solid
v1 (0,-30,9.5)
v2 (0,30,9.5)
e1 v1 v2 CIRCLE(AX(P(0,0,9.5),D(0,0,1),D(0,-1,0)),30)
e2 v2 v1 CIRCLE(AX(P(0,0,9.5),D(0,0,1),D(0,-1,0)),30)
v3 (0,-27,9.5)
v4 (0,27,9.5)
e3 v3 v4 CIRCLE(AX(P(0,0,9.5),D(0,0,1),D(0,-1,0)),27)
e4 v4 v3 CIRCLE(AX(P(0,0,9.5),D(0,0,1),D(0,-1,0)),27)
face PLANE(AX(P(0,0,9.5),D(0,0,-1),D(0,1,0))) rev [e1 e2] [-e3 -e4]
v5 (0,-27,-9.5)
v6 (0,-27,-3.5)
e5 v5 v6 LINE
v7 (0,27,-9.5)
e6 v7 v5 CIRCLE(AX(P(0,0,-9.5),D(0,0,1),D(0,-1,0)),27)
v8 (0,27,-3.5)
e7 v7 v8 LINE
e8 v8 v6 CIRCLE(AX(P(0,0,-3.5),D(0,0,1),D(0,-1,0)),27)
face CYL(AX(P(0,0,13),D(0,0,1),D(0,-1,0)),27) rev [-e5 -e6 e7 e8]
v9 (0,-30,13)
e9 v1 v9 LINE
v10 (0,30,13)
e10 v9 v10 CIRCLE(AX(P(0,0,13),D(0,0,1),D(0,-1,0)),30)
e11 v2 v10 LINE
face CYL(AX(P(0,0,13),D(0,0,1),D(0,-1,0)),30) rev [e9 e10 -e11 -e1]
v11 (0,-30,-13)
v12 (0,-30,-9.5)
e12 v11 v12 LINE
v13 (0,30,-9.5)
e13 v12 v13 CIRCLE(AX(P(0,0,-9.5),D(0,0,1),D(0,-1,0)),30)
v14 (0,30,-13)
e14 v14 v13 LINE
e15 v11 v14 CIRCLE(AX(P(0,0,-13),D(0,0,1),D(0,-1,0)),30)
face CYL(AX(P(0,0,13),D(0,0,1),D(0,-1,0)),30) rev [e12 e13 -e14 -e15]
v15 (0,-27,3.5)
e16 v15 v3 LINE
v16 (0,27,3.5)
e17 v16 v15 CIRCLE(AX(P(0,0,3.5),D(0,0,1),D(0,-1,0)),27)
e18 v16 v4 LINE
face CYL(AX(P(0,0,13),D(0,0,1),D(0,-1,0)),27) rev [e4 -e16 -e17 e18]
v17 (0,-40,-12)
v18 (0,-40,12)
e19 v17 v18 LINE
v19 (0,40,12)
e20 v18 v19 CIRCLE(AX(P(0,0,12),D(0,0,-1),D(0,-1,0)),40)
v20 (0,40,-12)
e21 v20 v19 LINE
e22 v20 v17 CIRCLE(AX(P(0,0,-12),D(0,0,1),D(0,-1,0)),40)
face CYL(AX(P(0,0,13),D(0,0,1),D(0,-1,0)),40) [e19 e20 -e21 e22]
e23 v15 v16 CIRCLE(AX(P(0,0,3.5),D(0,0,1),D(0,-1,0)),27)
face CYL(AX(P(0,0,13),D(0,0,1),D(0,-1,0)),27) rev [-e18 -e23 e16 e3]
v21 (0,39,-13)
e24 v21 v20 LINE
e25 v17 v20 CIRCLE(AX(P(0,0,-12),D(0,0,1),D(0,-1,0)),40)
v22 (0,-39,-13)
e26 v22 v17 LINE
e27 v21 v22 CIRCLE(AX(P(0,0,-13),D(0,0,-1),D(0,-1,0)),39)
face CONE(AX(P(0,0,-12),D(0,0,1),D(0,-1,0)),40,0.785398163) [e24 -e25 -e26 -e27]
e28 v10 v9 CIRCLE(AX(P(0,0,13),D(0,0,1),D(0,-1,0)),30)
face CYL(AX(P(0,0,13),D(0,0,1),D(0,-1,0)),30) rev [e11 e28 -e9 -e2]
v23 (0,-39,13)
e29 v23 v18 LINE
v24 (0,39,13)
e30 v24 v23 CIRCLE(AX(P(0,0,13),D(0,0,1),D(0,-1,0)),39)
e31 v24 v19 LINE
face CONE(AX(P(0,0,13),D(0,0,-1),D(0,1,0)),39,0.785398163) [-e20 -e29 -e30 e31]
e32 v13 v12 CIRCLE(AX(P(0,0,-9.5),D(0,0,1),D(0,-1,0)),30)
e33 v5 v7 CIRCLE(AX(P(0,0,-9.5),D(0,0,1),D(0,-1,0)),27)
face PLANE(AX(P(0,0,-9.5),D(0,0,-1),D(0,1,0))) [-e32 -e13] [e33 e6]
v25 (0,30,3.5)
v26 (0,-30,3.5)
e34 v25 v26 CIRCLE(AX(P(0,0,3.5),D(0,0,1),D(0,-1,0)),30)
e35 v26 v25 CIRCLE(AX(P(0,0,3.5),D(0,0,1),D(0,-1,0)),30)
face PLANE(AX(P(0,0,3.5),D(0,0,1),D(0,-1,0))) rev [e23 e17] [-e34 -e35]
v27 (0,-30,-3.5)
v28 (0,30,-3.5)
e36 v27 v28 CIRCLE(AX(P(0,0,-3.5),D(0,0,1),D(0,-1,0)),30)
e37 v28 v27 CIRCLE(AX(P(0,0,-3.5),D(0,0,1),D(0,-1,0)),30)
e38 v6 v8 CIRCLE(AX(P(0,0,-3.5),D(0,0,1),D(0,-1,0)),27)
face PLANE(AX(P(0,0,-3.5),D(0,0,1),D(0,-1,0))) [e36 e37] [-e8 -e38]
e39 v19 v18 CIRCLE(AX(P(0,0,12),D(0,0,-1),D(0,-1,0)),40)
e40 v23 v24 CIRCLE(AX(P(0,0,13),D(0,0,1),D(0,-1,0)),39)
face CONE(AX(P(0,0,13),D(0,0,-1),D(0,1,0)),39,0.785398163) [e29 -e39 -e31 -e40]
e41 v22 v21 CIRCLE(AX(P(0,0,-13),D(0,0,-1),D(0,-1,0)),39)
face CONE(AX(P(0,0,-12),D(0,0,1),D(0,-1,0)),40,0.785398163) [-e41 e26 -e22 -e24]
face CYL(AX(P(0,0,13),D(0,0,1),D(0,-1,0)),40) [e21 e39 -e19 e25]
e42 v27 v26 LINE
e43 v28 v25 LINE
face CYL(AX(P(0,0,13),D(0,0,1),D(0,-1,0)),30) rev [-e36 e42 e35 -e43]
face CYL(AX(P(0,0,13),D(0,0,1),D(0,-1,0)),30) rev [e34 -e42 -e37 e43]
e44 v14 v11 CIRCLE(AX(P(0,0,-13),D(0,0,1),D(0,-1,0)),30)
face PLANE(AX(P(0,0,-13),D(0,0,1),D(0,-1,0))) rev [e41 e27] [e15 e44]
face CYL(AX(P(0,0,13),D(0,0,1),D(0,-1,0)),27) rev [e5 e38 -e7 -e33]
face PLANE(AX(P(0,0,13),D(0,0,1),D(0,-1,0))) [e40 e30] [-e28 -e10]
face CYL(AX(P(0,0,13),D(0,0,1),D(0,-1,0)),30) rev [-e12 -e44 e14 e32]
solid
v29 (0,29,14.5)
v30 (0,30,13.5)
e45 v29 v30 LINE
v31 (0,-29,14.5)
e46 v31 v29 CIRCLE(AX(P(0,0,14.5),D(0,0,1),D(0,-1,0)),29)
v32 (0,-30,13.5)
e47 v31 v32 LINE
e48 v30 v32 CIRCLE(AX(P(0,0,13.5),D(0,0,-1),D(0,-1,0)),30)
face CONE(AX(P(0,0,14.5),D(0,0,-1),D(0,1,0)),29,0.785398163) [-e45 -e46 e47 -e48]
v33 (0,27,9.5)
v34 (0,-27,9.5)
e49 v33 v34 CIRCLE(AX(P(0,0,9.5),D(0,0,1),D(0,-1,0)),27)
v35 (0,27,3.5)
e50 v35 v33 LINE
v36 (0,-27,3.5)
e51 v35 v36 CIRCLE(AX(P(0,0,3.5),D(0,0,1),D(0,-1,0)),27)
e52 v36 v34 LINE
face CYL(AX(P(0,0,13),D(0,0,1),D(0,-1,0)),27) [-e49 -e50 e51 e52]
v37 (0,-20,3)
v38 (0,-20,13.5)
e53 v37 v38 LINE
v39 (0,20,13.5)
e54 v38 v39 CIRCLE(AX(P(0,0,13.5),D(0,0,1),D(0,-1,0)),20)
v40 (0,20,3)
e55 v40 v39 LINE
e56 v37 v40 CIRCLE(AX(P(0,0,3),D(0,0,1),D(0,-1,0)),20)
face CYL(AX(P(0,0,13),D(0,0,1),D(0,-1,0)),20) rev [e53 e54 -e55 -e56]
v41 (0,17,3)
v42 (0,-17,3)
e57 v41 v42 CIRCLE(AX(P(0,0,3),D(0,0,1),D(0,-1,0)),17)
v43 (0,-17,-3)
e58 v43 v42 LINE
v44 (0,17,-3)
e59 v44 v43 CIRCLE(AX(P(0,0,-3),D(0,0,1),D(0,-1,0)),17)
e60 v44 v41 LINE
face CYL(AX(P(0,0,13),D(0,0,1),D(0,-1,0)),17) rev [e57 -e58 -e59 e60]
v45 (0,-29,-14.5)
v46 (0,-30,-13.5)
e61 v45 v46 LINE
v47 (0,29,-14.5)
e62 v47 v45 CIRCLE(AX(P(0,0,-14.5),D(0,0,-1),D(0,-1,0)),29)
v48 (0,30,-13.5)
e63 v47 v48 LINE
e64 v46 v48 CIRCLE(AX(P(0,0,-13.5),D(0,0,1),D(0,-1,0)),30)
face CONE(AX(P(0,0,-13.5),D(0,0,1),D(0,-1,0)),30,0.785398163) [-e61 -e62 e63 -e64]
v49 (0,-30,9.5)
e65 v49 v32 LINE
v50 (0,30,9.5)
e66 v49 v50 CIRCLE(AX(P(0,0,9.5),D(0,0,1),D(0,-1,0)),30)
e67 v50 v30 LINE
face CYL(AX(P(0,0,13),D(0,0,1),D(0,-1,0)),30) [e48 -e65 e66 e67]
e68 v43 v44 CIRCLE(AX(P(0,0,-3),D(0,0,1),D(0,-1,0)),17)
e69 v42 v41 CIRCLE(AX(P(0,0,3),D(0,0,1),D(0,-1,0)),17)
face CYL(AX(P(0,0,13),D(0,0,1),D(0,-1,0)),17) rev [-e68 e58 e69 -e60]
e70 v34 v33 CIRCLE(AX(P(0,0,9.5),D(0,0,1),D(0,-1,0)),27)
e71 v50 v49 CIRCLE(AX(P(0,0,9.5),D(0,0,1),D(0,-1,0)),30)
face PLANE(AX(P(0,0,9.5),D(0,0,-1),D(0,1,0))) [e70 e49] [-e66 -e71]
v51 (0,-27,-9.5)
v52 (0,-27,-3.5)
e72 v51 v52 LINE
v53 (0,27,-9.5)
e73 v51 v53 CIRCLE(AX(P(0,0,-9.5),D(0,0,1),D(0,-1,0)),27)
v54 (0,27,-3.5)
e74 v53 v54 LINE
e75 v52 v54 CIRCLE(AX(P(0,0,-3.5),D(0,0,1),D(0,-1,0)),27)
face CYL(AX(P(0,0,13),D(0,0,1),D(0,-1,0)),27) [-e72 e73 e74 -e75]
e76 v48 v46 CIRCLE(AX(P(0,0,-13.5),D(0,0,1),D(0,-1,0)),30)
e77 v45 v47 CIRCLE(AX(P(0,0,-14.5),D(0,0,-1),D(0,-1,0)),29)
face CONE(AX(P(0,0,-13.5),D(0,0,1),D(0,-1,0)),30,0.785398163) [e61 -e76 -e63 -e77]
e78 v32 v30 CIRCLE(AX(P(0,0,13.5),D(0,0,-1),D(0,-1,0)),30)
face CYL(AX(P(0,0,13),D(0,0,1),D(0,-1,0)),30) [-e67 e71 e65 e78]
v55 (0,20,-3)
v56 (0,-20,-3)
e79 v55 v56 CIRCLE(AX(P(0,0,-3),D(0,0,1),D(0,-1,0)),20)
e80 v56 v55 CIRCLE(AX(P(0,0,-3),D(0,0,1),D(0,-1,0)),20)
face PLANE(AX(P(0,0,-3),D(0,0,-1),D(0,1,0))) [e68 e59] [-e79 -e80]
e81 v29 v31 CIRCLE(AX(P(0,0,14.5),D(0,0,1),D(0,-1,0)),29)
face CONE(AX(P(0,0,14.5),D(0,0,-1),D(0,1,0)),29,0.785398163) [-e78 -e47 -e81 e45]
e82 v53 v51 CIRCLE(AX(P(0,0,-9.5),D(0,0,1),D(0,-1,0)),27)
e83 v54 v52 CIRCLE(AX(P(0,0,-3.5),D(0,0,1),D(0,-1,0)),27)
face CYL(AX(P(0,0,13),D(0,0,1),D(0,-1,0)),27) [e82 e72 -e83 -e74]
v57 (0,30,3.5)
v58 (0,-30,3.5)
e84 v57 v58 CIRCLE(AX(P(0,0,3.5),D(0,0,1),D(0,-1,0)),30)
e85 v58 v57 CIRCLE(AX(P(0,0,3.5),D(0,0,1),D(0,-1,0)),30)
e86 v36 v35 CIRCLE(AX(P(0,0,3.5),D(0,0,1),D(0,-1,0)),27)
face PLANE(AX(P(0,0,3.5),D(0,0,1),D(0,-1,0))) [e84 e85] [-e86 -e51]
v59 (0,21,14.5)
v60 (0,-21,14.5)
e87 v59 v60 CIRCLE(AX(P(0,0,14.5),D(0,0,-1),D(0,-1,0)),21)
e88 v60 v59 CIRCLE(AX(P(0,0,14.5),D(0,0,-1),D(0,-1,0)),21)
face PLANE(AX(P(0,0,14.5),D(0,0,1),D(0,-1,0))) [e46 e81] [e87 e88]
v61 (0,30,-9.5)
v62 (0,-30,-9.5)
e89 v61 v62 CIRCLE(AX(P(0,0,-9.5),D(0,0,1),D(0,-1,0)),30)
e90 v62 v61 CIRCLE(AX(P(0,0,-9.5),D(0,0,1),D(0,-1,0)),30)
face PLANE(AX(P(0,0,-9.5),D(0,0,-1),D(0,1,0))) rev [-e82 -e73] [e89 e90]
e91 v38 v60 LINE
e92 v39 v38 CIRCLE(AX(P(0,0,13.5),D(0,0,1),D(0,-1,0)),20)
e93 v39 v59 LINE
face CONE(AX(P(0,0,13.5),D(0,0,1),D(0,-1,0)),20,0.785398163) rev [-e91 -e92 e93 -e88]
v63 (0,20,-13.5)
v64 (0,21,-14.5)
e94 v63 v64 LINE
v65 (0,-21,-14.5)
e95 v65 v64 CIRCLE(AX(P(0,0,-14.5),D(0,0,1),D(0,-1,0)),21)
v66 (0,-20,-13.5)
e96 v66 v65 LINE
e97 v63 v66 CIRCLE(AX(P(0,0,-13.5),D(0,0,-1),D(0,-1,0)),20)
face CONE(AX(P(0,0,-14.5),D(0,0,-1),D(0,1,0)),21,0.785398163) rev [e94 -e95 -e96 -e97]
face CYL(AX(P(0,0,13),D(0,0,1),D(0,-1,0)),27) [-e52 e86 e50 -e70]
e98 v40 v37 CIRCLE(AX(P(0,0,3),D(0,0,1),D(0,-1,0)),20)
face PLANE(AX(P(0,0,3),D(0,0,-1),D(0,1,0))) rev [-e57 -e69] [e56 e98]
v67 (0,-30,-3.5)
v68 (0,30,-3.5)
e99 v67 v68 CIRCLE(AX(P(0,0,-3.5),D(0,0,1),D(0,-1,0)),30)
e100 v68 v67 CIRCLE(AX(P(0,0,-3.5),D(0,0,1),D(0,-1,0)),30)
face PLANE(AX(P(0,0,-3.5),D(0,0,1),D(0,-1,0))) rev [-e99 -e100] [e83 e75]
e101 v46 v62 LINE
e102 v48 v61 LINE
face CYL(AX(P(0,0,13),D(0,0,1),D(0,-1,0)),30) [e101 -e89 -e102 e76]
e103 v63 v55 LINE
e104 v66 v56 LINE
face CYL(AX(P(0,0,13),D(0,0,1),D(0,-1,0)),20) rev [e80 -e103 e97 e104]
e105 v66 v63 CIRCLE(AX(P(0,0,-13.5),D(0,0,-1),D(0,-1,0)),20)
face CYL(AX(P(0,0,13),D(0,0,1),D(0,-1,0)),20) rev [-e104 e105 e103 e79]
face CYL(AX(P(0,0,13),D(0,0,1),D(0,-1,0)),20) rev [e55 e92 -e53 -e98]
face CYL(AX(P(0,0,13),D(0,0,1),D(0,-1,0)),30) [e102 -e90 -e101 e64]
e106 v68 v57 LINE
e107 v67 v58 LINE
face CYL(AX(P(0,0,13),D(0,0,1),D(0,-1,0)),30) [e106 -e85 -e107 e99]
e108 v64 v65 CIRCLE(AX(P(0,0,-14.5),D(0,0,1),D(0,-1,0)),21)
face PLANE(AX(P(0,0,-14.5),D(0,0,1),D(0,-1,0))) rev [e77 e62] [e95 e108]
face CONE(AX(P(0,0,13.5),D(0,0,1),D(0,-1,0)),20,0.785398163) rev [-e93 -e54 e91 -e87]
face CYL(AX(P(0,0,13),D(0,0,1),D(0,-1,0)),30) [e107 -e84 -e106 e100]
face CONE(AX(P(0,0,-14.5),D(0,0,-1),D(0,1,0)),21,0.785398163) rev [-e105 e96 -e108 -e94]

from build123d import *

# Parameters (mm, degrees)
SKETCH_1_3_2_W = 1.5
SKETCH_1_3_2_H = 10
CHAMFER1_SIZE  = 1
CHAMFER2_SIZE  = 1


with BuildPart() as part:
    # Sketch 1_3 → Revolve1 (revolve)
    with BuildSketch(Plane(origin=(0, 0, 0), x_dir=(0, 0, -1), z_dir=(1, 0, 0)), mode=Mode.PRIVATE) as revolve1_sk:
        Polygon((-13, 40), (-13, 30), (-9.5, 30), (-9.5, 27), (-3.5, 27), (-3.5, 30), (3.5, 30), (3.5, 27), (9.5, 27), (9.5, 30), (13, 30), (13, 40), align=None)
    revolve(revolve1_sk.sketch.rotate(Axis((0, 0, 13), (0, 0, -1)), 180), axis=Axis((0, 0, 13), (0, 0, -1)))

    # Chamfer1
    chamfer1_edges = [part.edges().sort_by_distance(p)[0] for p in [
        (0, 40, 13),
        (0, 40, -13),
    ]]
    chamfer(chamfer1_edges, length=CHAMFER1_SIZE)


with BuildPart() as body_2:
    # Sketch 1_3 2 → Revolve2 (revolve)
    with BuildSketch(Plane(origin=(0, 0, 0), x_dir=(0, 0, -1), z_dir=(1, 0, 0)), mode=Mode.PRIVATE) as revolve2_sk:
        Polygon((-13, 30), (-13, 20), (-3, 20), (-3, 17), (3, 17), (3, 20), (13, 20), (13, 30), (9.5, 30), (9.5, 27), (3.5, 27), (3.5, 30), (-3.5, 30), (-3.5, 27), (-9.5, 27), (-9.5, 30), align=None)
        with Locations((-13.75, 25)):
            Rectangle(SKETCH_1_3_2_W, SKETCH_1_3_2_H)
        with Locations((13.75, 25)):
            Rectangle(SKETCH_1_3_2_W, SKETCH_1_3_2_H)
    revolve(revolve2_sk.sketch.rotate(Axis((0, 0, 13), (0, 0, -1)), 180), axis=Axis((0, 0, 13), (0, 0, -1)))

    # Chamfer2
    chamfer2_edges = [body_2.edges().sort_by_distance(p)[0] for p in [
        (0, 30, -14.5),
        (0, 20, -14.5),
        (0, 20, 14.5),
        (0, 30, 14.5),
    ]]
    chamfer(chamfer2_edges, length=CHAMFER2_SIZE)


solid = Compound([part.part, body_2.part])
